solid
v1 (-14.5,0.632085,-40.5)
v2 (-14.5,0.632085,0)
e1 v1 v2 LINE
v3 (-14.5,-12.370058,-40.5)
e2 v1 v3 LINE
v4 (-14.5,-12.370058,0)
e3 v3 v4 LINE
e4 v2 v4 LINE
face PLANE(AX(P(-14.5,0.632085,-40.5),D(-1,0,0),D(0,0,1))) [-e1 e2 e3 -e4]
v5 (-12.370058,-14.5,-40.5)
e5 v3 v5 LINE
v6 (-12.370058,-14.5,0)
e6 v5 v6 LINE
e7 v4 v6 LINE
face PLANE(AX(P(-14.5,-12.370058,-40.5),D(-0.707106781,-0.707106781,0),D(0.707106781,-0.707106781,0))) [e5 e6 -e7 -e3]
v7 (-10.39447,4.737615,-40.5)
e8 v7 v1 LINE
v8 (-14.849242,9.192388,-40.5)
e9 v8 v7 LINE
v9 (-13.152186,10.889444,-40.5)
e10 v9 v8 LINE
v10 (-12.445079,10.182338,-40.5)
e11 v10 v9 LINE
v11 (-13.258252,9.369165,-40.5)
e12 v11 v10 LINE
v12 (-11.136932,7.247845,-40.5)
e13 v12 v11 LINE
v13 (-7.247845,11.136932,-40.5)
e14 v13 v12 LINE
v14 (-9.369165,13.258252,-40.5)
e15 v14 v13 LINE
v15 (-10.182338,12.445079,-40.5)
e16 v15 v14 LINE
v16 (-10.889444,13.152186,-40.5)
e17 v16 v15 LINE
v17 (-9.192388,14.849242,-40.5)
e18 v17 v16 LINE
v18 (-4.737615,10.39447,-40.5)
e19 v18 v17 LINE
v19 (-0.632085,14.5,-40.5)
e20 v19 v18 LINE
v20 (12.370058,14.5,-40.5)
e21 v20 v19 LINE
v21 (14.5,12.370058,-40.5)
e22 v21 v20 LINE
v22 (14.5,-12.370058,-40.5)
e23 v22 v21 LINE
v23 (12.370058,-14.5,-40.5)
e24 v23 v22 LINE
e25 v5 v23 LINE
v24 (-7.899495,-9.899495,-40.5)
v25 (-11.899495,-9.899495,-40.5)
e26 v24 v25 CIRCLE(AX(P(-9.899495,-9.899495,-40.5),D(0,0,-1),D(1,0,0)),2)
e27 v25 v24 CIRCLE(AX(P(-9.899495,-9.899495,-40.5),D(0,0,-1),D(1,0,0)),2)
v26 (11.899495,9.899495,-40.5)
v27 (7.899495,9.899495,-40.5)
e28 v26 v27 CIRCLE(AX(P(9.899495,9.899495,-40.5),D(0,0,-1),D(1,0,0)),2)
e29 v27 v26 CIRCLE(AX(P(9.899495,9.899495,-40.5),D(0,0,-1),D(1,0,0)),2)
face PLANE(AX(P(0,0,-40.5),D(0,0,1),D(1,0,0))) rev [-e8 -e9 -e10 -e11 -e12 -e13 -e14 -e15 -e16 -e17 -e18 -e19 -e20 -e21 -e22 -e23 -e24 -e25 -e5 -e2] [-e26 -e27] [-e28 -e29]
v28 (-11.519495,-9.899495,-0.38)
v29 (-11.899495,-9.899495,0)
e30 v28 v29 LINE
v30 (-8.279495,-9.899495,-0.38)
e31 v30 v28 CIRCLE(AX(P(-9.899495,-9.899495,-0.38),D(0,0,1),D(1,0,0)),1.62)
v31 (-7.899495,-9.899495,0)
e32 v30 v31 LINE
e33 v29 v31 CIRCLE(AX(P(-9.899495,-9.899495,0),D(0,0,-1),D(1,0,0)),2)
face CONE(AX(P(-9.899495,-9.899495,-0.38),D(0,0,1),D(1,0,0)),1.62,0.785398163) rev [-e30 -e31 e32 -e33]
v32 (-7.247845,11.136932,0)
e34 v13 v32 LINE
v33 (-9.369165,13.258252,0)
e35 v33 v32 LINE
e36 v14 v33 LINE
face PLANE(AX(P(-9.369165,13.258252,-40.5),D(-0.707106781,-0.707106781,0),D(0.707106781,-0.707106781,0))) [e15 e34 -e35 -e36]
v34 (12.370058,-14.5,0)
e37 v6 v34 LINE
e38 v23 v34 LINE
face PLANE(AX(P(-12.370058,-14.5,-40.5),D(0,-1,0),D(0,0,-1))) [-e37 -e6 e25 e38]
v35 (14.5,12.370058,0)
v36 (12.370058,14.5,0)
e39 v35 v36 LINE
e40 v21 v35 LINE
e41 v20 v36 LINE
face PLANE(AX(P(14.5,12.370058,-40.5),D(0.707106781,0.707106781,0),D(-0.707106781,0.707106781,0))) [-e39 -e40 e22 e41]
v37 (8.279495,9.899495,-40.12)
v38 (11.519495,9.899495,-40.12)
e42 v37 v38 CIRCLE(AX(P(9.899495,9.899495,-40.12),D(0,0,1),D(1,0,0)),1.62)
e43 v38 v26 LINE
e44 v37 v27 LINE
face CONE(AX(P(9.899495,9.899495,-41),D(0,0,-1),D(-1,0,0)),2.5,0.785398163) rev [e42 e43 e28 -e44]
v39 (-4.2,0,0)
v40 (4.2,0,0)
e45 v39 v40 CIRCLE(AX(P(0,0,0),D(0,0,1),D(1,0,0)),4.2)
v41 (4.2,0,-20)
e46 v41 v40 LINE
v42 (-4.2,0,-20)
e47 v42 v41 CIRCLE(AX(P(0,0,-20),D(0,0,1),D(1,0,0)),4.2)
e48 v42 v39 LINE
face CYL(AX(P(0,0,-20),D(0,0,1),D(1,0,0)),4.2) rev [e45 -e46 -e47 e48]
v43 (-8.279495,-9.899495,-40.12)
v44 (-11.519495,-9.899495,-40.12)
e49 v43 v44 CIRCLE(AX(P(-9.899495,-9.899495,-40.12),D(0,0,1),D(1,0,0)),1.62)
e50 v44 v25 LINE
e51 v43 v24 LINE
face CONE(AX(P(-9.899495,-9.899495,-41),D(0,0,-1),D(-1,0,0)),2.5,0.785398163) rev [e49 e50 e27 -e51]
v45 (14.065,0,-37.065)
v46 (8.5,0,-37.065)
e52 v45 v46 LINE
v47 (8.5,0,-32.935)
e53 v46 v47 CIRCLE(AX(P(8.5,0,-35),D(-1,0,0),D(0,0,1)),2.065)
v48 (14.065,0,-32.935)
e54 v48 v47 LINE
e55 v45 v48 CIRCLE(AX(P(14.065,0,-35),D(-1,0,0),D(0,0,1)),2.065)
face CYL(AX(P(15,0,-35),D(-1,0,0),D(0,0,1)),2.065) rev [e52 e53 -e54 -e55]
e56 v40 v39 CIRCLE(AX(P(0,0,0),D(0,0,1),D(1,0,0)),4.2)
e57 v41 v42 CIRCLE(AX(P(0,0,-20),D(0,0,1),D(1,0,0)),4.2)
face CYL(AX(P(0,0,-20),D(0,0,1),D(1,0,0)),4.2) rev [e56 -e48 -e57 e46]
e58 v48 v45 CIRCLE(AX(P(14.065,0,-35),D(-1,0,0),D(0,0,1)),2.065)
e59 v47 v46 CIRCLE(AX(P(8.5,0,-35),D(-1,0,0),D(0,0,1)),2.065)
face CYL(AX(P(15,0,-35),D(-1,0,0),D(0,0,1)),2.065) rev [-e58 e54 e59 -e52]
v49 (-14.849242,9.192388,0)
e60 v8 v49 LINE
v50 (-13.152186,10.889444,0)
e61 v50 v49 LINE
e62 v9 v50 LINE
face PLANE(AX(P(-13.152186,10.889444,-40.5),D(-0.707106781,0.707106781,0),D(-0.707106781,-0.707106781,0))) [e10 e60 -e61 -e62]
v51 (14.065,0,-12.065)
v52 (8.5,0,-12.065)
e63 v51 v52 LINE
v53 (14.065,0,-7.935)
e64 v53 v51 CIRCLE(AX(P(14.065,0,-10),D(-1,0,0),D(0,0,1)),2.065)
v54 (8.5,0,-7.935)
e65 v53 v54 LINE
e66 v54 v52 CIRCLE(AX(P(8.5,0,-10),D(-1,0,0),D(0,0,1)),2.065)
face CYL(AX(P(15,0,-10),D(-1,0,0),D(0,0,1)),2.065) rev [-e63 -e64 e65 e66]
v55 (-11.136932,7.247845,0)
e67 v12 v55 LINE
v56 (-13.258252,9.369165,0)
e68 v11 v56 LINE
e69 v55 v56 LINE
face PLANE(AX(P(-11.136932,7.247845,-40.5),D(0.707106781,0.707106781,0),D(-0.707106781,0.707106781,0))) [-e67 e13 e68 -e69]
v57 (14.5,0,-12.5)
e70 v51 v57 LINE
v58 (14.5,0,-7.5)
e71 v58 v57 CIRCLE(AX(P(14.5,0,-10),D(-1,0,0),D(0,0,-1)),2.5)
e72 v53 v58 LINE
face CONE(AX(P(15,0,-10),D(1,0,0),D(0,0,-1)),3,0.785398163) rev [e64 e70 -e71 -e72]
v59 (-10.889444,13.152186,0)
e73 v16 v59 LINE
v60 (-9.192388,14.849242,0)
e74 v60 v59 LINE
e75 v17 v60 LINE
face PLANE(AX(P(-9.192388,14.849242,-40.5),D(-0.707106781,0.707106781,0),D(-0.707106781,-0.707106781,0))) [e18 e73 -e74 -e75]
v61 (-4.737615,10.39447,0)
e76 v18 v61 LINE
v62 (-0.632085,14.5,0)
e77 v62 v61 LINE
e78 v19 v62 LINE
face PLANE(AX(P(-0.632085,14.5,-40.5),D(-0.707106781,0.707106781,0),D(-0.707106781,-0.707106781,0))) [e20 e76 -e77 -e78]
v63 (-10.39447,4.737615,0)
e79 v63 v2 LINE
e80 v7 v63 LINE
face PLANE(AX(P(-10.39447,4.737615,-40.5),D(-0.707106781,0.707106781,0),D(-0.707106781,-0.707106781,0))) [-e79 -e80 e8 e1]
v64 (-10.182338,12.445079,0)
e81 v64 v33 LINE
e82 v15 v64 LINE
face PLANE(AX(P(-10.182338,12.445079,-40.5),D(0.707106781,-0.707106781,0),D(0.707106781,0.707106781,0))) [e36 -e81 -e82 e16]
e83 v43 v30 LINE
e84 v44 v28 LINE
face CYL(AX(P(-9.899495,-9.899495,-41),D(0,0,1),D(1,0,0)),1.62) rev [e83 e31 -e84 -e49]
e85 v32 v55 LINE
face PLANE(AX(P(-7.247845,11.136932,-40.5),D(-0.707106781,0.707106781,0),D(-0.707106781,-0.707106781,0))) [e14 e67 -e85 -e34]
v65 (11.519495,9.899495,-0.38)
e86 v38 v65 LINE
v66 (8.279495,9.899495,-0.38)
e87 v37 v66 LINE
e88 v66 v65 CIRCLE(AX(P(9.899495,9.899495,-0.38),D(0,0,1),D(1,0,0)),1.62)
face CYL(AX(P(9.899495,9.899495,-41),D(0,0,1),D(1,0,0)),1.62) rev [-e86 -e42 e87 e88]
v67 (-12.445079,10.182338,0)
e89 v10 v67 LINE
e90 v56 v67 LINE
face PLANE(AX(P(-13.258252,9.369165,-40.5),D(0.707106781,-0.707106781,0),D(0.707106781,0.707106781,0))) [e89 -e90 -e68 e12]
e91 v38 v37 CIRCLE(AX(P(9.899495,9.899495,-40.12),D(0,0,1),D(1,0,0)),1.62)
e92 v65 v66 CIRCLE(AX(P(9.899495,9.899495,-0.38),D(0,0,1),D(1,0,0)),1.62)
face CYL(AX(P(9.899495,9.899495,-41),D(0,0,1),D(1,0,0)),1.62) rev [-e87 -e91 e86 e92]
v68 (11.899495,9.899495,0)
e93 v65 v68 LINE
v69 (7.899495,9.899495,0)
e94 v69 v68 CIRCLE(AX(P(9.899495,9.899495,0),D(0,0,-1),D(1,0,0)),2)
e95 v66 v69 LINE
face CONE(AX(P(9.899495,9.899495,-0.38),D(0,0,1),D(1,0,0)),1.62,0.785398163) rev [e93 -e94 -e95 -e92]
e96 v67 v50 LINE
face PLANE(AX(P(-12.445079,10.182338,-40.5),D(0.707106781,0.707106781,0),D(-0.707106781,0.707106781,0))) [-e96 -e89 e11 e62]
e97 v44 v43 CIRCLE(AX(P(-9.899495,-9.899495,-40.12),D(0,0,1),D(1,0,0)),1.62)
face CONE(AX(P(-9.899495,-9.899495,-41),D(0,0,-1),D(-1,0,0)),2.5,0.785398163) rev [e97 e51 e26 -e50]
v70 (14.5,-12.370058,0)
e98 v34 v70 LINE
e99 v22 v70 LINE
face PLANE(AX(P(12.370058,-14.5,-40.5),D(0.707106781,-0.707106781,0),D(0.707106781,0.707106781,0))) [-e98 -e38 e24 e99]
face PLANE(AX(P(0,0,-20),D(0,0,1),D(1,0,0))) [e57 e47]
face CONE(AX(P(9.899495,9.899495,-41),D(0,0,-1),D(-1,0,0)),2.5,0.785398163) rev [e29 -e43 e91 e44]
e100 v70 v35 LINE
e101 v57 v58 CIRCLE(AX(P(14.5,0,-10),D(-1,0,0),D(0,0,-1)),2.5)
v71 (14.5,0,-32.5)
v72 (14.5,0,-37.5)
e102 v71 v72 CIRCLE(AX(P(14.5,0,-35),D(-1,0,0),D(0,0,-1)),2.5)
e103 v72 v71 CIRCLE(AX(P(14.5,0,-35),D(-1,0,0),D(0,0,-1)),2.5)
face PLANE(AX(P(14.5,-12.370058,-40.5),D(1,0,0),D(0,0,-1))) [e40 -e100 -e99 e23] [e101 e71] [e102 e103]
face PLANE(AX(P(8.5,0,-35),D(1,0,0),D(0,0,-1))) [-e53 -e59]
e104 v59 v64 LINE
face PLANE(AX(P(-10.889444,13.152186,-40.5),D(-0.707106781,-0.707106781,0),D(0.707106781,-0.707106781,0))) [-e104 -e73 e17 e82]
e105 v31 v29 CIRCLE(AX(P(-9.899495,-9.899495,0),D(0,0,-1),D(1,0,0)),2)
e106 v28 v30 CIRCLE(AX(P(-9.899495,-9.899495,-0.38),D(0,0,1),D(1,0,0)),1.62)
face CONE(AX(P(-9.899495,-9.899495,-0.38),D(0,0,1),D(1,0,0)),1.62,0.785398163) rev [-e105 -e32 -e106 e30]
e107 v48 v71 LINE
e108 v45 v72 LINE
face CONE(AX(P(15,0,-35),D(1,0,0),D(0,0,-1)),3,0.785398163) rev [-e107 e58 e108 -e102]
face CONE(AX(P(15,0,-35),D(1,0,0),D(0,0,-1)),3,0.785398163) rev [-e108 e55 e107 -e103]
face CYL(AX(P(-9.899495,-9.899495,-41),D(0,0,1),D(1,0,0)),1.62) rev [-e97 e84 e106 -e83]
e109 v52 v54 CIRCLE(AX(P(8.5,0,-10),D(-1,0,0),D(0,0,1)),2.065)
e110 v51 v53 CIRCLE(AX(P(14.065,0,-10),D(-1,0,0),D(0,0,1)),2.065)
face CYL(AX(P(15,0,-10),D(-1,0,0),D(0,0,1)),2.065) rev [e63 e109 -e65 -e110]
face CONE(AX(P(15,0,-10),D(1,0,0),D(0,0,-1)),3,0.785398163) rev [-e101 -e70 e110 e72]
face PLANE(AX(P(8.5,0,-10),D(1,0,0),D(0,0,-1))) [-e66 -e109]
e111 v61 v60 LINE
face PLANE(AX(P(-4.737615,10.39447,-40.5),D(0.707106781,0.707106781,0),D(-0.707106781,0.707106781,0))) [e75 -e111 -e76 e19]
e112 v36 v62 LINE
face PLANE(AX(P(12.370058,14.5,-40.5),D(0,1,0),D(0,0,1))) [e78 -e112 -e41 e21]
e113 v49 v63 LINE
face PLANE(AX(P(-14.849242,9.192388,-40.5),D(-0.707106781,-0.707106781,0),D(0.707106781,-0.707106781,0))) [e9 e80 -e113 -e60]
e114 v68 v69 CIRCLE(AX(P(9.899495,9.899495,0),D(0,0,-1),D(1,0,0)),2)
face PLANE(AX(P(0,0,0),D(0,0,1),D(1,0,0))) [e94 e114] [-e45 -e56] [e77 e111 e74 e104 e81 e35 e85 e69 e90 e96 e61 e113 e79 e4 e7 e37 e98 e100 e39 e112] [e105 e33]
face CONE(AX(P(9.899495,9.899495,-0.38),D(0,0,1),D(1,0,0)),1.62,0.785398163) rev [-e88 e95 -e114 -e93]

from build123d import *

# Parameters (mm, degrees)
EXTRUDE_1_DEPTH     = 40.5
SKETCH_6_R          = 4.2
CUT_EXTRUDE_1_DEPTH = 20


with BuildPart() as part:
    # 草图1 → 凸台-拉伸1 (new body)
    with BuildSketch(Plane.XY):
        Polygon((-14.849242405, 9.192388155), (-10.394469683, 4.737615434), (-14.5, 0.632085117), (-14.5, -12.370057685), (-12.370057685, -14.5), (12.370057685, -14.5), (14.5, -12.370057685), (14.5, 12.370057685), (12.370057685, 14.5), (-0.632085117, 14.5), (-4.737615434, 10.394469683), (-9.192388155, 14.849242405), (-10.88944443, 13.15218613), (-10.182337649, 12.445079349), (-9.369164851, 13.258252147), (-7.247844507, 11.136931804), (-11.136931804, 7.247844507), (-13.258252147, 9.369164851), (-12.445079349, 10.182337649), (-13.15218613, 10.88944443), align=None)
    extrude(amount=-EXTRUDE_1_DEPTH)

    # 草图2 → 切除-旋转1 (revolve, cut)
    with BuildSketch(Plane(origin=(0, 0, 0), x_dir=(1, 0, 0), z_dir=(0, 1, 0)), mode=Mode.PRIVATE) as cut_revolve_1_sk:
        Polygon((8.5, 10), (8.5, 12.065), (14.065, 12.065), (15, 13), (15, 10), align=None)
    revolve(cut_revolve_1_sk.sketch.rotate(Axis((15, 0, -10), (-1, 0, 0)), 180), axis=Axis((15, 0, -10), (-1, 0, 0)), mode=Mode.SUBTRACT)

    # 草图3 → 切除-旋转2 (revolve, cut)
    with BuildSketch(Plane(origin=(0, 0, 0), x_dir=(1, 0, 0), z_dir=(0, 1, 0)), mode=Mode.PRIVATE) as cut_revolve_2_sk:
        Polygon((8.5, 35), (8.5, 37.065), (14.065, 37.065), (15, 38), (15, 35), align=None)
    revolve(cut_revolve_2_sk.sketch.rotate(Axis((15, 0, -35), (-1, 0, 0)), 180), axis=Axis((15, 0, -35), (-1, 0, 0)), mode=Mode.SUBTRACT)

    # 草图4 → 切除-旋转3 (revolve, cut)
    with BuildSketch(Plane(origin=(0, 0, 0), x_dir=(-0.7071067811865475, -0.7071067811865477, 0), z_dir=(0.7071067811865477, -0.7071067811865475, 0)), mode=Mode.PRIVATE) as cut_revolve_3_sk:
        Polygon((-14, -0.5), (-16.5, -0.5), (-15.62, 0.38), (-15.62, 40.12), (-16.5, 41), (-14, 41), align=None)
    revolve(cut_revolve_3_sk.sketch.rotate(Axis((9.899494937, 9.899494937, -41), (0, 0, 1)), 315), axis=Axis((9.899494937, 9.899494937, -41), (0, 0, 1)), mode=Mode.SUBTRACT)

    # 草图5 → 切除-旋转4 (revolve, cut)
    with BuildSketch(Plane(origin=(0, 0, 0), x_dir=(-0.7071067811865475, -0.7071067811865477, 0), z_dir=(0.7071067811865477, -0.7071067811865475, 0)), mode=Mode.PRIVATE) as cut_revolve_4_sk:
        Polygon((14, -0.5), (11.5, -0.5), (12.38, 0.38), (12.38, 40.12), (11.5, 41), (14, 41), align=None)
    revolve(cut_revolve_4_sk.sketch.rotate(Axis((-9.899494937, -9.899494937, -41), (0, 0, 1)), 315), axis=Axis((-9.899494937, -9.899494937, -41), (0, 0, 1)), mode=Mode.SUBTRACT)

    # 草图6 → 切除-拉伸1 (cut)
    with BuildSketch(Plane.XY):
        Circle(SKETCH_6_R)
    extrude(amount=-CUT_EXTRUDE_1_DEPTH, mode=Mode.SUBTRACT)


solid = part.part
